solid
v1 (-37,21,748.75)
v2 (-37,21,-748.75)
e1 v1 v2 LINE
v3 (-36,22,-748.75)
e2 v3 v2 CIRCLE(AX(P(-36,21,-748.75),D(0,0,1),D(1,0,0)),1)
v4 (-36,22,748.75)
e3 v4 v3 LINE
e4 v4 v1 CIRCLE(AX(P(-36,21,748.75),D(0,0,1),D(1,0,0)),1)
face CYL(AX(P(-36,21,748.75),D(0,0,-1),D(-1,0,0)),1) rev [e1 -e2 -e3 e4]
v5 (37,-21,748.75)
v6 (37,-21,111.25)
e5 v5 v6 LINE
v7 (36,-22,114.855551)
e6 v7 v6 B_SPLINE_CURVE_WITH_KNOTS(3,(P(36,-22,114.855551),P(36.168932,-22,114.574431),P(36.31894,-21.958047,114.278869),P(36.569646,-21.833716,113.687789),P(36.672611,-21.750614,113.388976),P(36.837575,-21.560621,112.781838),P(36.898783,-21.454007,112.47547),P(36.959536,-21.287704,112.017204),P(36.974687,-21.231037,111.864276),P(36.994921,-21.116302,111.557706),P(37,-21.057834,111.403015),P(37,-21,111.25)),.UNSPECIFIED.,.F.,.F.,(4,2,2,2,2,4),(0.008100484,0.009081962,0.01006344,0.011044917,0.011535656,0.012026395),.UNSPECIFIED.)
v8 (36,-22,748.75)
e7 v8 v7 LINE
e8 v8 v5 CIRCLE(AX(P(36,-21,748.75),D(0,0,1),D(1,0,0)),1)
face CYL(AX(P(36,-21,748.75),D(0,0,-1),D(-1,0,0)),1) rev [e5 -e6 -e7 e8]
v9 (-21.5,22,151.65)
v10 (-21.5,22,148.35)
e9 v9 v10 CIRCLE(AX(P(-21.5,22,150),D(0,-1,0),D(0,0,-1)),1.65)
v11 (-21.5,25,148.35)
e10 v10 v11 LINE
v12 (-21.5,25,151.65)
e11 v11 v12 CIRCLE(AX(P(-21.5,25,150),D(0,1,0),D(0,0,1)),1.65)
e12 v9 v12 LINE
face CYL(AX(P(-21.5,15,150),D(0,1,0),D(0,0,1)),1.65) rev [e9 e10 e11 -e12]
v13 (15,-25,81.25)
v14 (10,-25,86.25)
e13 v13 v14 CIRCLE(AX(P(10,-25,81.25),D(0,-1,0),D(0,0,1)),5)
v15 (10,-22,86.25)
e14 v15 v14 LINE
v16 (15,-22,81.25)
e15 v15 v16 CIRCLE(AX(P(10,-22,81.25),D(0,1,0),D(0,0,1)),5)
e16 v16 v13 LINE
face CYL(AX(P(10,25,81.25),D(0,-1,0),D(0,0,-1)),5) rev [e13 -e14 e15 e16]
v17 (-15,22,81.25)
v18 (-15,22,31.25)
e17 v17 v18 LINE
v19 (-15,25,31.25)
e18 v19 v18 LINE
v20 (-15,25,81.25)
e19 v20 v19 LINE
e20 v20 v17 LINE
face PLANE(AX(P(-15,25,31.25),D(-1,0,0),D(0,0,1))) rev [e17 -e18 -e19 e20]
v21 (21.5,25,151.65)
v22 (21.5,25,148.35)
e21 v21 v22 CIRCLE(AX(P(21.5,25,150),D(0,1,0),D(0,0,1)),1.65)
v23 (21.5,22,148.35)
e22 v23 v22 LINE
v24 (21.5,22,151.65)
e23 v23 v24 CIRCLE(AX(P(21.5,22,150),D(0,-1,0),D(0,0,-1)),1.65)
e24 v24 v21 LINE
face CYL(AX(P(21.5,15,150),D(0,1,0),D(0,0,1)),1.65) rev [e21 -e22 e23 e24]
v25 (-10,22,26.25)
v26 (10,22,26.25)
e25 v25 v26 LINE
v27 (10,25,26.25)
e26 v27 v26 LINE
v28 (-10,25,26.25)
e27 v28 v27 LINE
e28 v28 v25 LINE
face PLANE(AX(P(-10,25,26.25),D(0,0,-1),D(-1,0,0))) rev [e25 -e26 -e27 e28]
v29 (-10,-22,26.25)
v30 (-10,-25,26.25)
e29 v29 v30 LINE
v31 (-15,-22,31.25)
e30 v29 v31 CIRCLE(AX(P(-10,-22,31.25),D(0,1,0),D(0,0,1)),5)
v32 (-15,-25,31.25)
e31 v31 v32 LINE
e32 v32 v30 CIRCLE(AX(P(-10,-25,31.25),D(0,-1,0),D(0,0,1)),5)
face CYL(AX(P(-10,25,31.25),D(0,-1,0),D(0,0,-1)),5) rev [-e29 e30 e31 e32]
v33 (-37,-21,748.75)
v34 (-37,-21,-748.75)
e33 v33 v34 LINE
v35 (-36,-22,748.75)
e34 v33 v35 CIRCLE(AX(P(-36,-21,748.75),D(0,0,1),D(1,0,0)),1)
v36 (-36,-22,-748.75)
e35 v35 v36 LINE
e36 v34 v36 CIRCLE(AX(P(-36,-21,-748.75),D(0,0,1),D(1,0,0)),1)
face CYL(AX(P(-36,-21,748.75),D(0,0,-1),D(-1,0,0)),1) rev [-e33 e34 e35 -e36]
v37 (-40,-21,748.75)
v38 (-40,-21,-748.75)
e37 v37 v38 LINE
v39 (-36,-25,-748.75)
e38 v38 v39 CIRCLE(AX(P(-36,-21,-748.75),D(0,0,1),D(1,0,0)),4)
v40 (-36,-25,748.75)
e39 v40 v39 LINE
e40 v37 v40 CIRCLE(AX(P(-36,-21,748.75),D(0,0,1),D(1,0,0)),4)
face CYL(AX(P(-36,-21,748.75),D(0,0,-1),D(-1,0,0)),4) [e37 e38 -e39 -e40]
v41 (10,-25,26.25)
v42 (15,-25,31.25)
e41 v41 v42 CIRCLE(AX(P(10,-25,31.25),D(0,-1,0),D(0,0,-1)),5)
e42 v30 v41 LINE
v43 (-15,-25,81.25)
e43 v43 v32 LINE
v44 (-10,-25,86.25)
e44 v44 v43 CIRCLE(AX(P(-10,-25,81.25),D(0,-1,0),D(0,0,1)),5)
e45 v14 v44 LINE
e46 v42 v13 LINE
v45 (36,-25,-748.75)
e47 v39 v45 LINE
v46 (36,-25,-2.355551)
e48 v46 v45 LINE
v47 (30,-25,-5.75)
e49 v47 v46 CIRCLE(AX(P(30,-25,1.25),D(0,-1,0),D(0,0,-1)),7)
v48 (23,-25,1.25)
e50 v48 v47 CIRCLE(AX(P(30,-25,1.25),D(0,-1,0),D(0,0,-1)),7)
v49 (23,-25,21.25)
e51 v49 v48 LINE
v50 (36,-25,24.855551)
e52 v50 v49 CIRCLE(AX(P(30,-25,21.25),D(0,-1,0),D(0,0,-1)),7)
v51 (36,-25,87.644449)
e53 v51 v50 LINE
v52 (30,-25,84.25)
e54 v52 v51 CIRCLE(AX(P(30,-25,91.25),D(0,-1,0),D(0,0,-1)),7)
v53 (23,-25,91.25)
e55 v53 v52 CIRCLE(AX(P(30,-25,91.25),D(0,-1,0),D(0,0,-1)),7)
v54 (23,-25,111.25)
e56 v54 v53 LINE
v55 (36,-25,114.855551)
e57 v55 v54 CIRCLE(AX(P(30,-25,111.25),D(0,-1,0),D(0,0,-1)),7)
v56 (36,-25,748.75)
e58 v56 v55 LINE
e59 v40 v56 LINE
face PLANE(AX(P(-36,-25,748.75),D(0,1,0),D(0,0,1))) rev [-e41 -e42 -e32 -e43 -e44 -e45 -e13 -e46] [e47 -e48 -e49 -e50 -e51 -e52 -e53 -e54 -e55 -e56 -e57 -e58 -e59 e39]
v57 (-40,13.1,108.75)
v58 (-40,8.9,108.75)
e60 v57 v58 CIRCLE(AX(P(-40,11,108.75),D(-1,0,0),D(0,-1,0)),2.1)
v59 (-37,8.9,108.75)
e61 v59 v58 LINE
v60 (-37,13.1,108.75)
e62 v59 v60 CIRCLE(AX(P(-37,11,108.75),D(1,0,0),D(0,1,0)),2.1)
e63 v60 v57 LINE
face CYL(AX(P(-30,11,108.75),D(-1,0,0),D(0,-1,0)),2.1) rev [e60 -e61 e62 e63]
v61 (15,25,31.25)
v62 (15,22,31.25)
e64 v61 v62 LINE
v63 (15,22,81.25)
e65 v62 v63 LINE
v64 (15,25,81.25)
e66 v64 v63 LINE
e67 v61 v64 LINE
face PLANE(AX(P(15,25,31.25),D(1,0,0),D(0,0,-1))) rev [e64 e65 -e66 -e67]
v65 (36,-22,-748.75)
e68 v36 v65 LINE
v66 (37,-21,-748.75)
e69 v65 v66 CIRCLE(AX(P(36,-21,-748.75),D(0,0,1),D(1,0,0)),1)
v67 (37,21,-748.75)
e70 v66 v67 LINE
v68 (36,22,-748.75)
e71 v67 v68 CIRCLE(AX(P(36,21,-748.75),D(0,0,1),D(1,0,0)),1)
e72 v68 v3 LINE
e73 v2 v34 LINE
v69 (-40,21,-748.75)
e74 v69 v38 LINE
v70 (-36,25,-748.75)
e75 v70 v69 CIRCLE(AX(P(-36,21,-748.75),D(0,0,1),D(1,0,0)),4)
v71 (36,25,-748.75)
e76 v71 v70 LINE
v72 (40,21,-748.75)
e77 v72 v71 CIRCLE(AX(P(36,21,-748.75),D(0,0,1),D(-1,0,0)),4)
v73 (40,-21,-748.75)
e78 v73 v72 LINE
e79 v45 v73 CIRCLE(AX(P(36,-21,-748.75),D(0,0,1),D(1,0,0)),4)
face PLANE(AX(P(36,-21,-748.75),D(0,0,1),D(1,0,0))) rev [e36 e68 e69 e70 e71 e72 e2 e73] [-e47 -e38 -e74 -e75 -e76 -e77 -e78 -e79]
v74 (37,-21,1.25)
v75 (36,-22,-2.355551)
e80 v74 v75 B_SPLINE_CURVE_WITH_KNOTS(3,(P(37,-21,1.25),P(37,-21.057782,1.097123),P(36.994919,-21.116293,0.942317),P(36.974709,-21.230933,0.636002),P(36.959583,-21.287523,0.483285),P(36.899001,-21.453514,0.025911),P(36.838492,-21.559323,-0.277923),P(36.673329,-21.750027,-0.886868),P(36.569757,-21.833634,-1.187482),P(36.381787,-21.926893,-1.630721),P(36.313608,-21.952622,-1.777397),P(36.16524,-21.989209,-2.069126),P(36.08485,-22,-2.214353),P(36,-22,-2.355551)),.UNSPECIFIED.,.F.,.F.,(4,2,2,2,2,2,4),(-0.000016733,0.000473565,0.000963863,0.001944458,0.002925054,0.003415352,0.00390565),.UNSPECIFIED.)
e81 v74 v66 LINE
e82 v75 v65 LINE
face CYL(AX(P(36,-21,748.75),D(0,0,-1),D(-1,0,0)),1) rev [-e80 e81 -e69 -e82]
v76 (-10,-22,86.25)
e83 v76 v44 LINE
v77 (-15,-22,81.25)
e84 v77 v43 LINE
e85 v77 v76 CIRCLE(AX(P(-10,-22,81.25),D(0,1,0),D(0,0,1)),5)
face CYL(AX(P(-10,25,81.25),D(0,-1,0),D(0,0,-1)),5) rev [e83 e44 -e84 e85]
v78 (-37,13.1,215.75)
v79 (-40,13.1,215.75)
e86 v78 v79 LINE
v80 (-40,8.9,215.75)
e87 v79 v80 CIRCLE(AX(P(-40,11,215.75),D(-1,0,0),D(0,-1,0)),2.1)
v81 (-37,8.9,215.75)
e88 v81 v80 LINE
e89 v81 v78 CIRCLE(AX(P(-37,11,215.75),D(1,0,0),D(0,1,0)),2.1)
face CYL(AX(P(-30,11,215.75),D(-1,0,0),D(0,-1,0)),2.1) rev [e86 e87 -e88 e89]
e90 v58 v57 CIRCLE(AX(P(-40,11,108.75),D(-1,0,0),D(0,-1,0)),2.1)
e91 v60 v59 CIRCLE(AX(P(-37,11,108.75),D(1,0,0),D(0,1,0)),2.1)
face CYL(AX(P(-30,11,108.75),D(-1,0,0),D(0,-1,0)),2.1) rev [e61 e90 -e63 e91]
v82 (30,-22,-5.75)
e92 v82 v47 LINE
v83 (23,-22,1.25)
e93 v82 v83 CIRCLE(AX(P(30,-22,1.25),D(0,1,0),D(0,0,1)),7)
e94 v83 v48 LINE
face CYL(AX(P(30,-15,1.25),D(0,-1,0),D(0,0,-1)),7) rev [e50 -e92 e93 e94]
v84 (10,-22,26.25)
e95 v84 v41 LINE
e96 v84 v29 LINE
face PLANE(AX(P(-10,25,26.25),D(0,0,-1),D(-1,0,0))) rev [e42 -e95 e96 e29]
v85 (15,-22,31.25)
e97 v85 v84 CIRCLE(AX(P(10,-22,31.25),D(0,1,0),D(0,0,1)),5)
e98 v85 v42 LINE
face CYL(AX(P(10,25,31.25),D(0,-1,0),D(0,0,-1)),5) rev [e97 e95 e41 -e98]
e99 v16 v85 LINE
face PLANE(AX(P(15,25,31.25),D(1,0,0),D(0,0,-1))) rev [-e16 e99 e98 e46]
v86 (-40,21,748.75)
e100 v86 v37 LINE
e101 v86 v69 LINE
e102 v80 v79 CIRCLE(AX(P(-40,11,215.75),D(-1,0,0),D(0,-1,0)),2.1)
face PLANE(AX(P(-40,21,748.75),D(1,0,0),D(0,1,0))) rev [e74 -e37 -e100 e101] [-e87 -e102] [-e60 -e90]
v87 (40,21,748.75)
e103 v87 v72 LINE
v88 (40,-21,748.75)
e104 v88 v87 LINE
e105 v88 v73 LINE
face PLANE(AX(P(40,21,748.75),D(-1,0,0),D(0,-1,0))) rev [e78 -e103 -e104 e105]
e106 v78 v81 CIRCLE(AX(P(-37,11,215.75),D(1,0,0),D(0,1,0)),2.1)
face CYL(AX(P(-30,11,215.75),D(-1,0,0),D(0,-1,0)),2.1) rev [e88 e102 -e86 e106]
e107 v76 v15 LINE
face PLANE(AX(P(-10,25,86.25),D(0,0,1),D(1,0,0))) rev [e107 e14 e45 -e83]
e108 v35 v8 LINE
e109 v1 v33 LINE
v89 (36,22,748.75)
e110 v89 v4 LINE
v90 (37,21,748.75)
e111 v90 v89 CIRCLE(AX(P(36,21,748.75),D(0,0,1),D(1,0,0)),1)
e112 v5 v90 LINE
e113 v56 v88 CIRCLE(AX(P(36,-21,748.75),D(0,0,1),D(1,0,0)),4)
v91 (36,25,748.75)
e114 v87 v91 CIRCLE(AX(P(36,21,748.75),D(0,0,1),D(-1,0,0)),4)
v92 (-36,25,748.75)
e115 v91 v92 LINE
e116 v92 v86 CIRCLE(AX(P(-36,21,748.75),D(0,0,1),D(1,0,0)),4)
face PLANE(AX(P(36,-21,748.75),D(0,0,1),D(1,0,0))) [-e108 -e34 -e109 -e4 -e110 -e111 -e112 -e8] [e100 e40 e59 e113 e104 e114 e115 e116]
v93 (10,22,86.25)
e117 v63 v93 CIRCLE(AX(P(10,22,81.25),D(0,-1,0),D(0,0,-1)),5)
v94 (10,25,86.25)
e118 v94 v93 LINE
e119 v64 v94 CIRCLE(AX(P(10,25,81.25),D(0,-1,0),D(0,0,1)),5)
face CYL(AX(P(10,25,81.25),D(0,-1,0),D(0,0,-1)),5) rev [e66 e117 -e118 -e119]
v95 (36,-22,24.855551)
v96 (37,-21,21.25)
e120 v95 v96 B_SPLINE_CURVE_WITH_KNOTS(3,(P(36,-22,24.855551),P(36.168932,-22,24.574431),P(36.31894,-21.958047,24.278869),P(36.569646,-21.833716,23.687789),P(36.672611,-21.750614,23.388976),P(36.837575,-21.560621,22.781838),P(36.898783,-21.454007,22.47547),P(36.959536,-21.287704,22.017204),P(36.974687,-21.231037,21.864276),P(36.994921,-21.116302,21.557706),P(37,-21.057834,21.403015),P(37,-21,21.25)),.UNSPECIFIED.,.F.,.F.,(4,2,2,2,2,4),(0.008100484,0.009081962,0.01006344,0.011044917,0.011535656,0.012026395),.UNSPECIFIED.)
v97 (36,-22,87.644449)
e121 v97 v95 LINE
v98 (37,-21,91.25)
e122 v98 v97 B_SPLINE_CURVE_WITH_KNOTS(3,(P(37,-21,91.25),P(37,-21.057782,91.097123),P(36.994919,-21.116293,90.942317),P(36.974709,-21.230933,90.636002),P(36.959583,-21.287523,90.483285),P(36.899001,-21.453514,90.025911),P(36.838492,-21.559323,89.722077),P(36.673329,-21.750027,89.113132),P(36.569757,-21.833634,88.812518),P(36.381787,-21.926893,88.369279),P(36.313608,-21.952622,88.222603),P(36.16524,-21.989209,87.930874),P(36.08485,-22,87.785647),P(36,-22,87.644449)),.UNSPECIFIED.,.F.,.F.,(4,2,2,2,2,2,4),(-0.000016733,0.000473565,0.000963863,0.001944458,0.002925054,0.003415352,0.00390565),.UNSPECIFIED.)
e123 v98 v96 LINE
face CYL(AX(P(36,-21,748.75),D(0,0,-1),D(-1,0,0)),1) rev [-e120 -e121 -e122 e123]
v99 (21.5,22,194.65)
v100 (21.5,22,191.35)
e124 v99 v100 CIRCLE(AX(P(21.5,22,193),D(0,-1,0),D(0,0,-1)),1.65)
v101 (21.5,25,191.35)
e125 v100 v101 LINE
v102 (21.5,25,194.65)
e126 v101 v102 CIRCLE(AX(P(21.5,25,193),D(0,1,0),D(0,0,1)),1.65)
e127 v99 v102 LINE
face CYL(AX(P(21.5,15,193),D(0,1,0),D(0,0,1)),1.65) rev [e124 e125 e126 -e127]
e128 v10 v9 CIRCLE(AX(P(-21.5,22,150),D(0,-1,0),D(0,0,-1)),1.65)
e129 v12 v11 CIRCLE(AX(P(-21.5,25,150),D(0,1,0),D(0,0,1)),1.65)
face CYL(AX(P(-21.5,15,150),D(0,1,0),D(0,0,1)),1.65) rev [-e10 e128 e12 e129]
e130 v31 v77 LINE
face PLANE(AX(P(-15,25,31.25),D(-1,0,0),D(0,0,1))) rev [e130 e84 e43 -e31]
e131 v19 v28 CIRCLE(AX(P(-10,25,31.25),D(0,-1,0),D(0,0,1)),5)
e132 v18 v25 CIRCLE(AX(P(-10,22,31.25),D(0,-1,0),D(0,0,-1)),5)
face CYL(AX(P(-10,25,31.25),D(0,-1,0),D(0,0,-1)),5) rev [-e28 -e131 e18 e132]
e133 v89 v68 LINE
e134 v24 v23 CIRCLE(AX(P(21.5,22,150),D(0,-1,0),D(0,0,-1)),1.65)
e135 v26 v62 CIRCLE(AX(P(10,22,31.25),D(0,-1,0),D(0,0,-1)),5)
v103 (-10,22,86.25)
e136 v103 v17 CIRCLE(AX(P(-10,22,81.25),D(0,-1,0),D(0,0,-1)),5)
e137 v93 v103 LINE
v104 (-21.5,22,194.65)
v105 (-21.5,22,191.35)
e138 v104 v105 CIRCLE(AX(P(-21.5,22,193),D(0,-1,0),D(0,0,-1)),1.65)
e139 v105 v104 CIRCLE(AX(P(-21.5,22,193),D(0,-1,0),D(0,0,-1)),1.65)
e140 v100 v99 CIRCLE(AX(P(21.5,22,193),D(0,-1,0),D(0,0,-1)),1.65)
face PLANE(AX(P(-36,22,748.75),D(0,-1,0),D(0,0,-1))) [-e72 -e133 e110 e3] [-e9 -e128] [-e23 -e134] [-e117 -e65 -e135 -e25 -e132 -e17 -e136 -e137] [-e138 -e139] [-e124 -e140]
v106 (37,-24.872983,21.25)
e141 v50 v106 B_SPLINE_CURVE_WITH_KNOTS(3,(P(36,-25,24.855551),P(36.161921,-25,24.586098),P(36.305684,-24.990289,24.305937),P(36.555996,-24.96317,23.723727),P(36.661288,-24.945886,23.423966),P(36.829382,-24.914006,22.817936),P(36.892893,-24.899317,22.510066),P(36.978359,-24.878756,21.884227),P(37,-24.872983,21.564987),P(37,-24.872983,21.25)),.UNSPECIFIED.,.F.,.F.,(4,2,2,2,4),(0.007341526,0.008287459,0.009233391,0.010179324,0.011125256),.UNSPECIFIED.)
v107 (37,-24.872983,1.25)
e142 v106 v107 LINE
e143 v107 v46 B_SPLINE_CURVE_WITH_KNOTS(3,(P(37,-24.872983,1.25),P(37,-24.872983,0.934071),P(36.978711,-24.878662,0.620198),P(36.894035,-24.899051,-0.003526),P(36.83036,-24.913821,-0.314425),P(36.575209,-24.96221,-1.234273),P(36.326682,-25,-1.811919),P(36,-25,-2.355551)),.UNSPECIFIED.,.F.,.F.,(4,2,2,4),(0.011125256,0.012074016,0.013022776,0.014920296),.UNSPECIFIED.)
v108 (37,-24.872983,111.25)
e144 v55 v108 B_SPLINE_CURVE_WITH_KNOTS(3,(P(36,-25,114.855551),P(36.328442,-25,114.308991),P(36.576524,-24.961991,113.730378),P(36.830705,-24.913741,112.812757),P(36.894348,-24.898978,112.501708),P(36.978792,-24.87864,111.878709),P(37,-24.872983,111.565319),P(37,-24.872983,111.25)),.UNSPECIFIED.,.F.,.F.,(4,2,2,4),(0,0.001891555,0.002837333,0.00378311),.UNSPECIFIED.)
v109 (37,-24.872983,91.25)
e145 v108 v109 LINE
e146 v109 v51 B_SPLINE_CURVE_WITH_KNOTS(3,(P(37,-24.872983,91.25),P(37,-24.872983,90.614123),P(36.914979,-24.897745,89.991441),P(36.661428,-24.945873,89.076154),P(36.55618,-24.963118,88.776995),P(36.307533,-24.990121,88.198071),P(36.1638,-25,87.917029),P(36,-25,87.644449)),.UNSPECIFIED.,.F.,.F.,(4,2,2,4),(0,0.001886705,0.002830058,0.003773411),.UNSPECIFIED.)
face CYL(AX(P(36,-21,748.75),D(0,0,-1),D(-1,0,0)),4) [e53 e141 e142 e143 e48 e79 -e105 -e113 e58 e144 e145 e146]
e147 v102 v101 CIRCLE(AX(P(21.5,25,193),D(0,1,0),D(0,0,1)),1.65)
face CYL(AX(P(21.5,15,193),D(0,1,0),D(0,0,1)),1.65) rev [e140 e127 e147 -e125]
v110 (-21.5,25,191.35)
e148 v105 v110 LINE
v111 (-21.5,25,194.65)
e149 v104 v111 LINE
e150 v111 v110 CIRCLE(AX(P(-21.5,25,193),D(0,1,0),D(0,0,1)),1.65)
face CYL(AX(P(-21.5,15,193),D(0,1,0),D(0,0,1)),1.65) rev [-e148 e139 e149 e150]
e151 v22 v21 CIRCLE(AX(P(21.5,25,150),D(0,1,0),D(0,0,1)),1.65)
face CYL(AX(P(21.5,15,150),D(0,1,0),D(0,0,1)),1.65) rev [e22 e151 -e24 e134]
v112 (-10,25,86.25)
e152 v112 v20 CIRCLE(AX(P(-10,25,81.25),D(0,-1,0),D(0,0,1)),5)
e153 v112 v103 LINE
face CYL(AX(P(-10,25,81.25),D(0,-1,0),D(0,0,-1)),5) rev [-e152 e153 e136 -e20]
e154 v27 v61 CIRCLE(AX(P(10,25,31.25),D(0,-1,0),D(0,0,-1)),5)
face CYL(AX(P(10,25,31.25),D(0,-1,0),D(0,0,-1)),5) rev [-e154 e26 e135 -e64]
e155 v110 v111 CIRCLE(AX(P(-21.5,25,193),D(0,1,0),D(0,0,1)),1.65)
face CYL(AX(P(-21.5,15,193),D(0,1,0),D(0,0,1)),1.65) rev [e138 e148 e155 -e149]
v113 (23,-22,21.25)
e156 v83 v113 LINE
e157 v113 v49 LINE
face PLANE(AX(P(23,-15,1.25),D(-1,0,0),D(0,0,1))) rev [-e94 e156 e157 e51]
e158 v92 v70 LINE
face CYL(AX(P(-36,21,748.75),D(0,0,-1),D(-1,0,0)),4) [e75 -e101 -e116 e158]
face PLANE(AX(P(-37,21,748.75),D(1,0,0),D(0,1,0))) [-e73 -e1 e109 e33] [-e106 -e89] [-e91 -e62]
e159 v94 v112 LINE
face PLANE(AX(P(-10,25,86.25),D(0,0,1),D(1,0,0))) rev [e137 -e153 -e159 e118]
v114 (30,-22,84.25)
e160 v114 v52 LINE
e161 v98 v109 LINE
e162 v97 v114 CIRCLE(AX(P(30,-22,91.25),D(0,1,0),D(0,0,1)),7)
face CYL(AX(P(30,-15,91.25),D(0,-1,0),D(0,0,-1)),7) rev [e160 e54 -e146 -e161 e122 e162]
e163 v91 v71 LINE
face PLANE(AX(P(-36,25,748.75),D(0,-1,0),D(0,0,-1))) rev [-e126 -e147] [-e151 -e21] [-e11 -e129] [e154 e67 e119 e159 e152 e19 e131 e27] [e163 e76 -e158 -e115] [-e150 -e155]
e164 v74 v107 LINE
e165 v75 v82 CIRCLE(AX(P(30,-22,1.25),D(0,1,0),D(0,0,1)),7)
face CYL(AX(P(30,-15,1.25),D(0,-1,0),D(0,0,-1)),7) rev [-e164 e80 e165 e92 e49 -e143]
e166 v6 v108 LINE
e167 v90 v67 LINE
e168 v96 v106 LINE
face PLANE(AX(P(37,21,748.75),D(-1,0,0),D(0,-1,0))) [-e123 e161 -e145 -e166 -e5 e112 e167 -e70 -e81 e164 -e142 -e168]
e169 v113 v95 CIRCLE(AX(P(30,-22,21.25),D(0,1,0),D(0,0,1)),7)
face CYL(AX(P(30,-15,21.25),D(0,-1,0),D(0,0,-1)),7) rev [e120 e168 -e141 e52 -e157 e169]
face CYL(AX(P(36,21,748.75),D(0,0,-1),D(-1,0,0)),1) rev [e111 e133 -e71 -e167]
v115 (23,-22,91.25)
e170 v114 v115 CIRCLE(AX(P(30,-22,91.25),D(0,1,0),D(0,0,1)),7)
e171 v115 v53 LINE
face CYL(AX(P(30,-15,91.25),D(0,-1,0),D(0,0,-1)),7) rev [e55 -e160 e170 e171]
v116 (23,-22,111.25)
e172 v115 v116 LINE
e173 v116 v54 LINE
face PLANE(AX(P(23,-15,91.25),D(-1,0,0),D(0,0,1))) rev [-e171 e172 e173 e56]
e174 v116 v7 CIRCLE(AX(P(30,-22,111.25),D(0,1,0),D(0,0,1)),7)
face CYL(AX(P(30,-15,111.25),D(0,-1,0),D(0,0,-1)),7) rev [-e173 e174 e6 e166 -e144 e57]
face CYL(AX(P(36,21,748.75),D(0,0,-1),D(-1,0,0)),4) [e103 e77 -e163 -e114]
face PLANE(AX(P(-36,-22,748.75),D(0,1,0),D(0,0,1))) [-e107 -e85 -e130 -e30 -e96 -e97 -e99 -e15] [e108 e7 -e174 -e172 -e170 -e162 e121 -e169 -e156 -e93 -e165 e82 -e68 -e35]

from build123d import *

# Parameters (mm, degrees)
EXTRUDE_1_DEPTH     = 748.75
CUT_EXTRUDE_2_DEPTH = 10
CUT_EXTRUDE_3_DEPTH = 752.482909092
SKETCH_6_R          = 1.65
CUT_EXTRUDE_4_DEPTH = 10
SKETCH_7_R          = 2.1
CUT_EXTRUDE_5_DEPTH = 10


with BuildPart() as part:
    # 草图1 → 拉伸-薄壁1 (new, symmetric)
    with BuildSketch(Plane.XY):
        with BuildLine():
            Line((-36, 25), (36, 25))
            ThreePointArc((36, 25), (38.828427125, 23.828427125), (40, 21))
            Line((40, 21), (40, -21))
            ThreePointArc((40, -21), (38.828427125, -23.828427125), (36, -25))
            Line((36, -25), (-36, -25))
            ThreePointArc((-36, -25), (-38.828427125, -23.828427125), (-40, -21))
            Line((-40, -21), (-40, 21))
            ThreePointArc((-40, 21), (-38.828427125, 23.828427125), (-36, 25))
        make_face()
        with BuildLine():
            Line((-36, 22), (36, 22))
            ThreePointArc((36, 22), (36.707106781, 21.707106781), (37, 21))
            Line((37, 21), (37, -21))
            ThreePointArc((37, -21), (36.707106781, -21.707106781), (36, -22))
            Line((36, -22), (-36, -22))
            ThreePointArc((-36, -22), (-36.707106781, -21.707106781), (-37, -21))
            Line((-37, -21), (-37, 21))
            ThreePointArc((-37, 21), (-36.707106781, 21.707106781), (-36, 22))
        make_face(mode=Mode.SUBTRACT)
    extrude(amount=EXTRUDE_1_DEPTH, both=True)

    # 草图4 → 切除-拉伸2 (cut)
    with BuildSketch(Plane.XZ.offset(25)):
        with BuildLine():
            Line((23, 91.25), (23, 111.25))
            ThreePointArc((23, 111.25), (30, 118.25), (37, 111.25))
            Line((37, 111.25), (37, 91.25))
            ThreePointArc((37, 91.25), (30, 84.25), (23, 91.25))
        make_face()
        with BuildLine():
            Line((23, 1.25), (23, 21.25))
            ThreePointArc((23, 21.25), (30, 28.25), (37, 21.25))
            Line((37, 21.25), (37, 1.25))
            ThreePointArc((37, 1.25), (30, -5.75), (23, 1.25))
        make_face()
    extrude(amount=-CUT_EXTRUDE_2_DEPTH, mode=Mode.SUBTRACT)

    # 草图5 → 切除-拉伸3 (cut, through all)
    with BuildSketch(Plane.XZ.offset(25)):
        with BuildLine():
            Line((-10, 26.25), (10, 26.25))
            ThreePointArc((10, 26.25), (13.535533906, 27.714466094), (15, 31.25))
            Line((15, 31.25), (15, 81.25))
            ThreePointArc((15, 81.25), (13.535533906, 84.785533906), (10, 86.25))
            Line((10, 86.25), (-10, 86.25))
            ThreePointArc((-10, 86.25), (-13.535533906, 84.785533906), (-15, 81.25))
            Line((-15, 81.25), (-15, 31.25))
            ThreePointArc((-15, 31.25), (-13.535533906, 27.714466094), (-10, 26.25))
        make_face()
    extrude(amount=-CUT_EXTRUDE_3_DEPTH, mode=Mode.SUBTRACT)

    # 草图6 → 切除-拉伸4 (cut)
    with BuildSketch(Plane(origin=(0, 25, 0), x_dir=(1, 0, 0), z_dir=(0, 1, 0))):
        with Locations(Location((-21.5, -150, 0), (0, 0, 270))):
            Circle(SKETCH_6_R)
        with Locations(Location((-21.5, -193, 0), (0, 0, 270))):
            Circle(SKETCH_6_R)
        with Locations(Location((21.5, -150, 0), (0, 0, 270))):
            Circle(SKETCH_6_R)
        with Locations(Location((21.5, -193, 0), (0, 0, 270))):
            Circle(SKETCH_6_R)
    extrude(amount=-CUT_EXTRUDE_4_DEPTH, mode=Mode.SUBTRACT)

    # 草图7 → 切除-拉伸5 (cut)
    with BuildSketch(Plane.ZY.offset(40)):
        with Locations(Location((108.75, 11, 0), (0, 0, 270))):
            Circle(SKETCH_7_R)
        with Locations(Location((215.75, 11, 0), (0, 0, 270))):
            Circle(SKETCH_7_R)
    extrude(amount=-CUT_EXTRUDE_5_DEPTH, mode=Mode.SUBTRACT)


solid = part.part
